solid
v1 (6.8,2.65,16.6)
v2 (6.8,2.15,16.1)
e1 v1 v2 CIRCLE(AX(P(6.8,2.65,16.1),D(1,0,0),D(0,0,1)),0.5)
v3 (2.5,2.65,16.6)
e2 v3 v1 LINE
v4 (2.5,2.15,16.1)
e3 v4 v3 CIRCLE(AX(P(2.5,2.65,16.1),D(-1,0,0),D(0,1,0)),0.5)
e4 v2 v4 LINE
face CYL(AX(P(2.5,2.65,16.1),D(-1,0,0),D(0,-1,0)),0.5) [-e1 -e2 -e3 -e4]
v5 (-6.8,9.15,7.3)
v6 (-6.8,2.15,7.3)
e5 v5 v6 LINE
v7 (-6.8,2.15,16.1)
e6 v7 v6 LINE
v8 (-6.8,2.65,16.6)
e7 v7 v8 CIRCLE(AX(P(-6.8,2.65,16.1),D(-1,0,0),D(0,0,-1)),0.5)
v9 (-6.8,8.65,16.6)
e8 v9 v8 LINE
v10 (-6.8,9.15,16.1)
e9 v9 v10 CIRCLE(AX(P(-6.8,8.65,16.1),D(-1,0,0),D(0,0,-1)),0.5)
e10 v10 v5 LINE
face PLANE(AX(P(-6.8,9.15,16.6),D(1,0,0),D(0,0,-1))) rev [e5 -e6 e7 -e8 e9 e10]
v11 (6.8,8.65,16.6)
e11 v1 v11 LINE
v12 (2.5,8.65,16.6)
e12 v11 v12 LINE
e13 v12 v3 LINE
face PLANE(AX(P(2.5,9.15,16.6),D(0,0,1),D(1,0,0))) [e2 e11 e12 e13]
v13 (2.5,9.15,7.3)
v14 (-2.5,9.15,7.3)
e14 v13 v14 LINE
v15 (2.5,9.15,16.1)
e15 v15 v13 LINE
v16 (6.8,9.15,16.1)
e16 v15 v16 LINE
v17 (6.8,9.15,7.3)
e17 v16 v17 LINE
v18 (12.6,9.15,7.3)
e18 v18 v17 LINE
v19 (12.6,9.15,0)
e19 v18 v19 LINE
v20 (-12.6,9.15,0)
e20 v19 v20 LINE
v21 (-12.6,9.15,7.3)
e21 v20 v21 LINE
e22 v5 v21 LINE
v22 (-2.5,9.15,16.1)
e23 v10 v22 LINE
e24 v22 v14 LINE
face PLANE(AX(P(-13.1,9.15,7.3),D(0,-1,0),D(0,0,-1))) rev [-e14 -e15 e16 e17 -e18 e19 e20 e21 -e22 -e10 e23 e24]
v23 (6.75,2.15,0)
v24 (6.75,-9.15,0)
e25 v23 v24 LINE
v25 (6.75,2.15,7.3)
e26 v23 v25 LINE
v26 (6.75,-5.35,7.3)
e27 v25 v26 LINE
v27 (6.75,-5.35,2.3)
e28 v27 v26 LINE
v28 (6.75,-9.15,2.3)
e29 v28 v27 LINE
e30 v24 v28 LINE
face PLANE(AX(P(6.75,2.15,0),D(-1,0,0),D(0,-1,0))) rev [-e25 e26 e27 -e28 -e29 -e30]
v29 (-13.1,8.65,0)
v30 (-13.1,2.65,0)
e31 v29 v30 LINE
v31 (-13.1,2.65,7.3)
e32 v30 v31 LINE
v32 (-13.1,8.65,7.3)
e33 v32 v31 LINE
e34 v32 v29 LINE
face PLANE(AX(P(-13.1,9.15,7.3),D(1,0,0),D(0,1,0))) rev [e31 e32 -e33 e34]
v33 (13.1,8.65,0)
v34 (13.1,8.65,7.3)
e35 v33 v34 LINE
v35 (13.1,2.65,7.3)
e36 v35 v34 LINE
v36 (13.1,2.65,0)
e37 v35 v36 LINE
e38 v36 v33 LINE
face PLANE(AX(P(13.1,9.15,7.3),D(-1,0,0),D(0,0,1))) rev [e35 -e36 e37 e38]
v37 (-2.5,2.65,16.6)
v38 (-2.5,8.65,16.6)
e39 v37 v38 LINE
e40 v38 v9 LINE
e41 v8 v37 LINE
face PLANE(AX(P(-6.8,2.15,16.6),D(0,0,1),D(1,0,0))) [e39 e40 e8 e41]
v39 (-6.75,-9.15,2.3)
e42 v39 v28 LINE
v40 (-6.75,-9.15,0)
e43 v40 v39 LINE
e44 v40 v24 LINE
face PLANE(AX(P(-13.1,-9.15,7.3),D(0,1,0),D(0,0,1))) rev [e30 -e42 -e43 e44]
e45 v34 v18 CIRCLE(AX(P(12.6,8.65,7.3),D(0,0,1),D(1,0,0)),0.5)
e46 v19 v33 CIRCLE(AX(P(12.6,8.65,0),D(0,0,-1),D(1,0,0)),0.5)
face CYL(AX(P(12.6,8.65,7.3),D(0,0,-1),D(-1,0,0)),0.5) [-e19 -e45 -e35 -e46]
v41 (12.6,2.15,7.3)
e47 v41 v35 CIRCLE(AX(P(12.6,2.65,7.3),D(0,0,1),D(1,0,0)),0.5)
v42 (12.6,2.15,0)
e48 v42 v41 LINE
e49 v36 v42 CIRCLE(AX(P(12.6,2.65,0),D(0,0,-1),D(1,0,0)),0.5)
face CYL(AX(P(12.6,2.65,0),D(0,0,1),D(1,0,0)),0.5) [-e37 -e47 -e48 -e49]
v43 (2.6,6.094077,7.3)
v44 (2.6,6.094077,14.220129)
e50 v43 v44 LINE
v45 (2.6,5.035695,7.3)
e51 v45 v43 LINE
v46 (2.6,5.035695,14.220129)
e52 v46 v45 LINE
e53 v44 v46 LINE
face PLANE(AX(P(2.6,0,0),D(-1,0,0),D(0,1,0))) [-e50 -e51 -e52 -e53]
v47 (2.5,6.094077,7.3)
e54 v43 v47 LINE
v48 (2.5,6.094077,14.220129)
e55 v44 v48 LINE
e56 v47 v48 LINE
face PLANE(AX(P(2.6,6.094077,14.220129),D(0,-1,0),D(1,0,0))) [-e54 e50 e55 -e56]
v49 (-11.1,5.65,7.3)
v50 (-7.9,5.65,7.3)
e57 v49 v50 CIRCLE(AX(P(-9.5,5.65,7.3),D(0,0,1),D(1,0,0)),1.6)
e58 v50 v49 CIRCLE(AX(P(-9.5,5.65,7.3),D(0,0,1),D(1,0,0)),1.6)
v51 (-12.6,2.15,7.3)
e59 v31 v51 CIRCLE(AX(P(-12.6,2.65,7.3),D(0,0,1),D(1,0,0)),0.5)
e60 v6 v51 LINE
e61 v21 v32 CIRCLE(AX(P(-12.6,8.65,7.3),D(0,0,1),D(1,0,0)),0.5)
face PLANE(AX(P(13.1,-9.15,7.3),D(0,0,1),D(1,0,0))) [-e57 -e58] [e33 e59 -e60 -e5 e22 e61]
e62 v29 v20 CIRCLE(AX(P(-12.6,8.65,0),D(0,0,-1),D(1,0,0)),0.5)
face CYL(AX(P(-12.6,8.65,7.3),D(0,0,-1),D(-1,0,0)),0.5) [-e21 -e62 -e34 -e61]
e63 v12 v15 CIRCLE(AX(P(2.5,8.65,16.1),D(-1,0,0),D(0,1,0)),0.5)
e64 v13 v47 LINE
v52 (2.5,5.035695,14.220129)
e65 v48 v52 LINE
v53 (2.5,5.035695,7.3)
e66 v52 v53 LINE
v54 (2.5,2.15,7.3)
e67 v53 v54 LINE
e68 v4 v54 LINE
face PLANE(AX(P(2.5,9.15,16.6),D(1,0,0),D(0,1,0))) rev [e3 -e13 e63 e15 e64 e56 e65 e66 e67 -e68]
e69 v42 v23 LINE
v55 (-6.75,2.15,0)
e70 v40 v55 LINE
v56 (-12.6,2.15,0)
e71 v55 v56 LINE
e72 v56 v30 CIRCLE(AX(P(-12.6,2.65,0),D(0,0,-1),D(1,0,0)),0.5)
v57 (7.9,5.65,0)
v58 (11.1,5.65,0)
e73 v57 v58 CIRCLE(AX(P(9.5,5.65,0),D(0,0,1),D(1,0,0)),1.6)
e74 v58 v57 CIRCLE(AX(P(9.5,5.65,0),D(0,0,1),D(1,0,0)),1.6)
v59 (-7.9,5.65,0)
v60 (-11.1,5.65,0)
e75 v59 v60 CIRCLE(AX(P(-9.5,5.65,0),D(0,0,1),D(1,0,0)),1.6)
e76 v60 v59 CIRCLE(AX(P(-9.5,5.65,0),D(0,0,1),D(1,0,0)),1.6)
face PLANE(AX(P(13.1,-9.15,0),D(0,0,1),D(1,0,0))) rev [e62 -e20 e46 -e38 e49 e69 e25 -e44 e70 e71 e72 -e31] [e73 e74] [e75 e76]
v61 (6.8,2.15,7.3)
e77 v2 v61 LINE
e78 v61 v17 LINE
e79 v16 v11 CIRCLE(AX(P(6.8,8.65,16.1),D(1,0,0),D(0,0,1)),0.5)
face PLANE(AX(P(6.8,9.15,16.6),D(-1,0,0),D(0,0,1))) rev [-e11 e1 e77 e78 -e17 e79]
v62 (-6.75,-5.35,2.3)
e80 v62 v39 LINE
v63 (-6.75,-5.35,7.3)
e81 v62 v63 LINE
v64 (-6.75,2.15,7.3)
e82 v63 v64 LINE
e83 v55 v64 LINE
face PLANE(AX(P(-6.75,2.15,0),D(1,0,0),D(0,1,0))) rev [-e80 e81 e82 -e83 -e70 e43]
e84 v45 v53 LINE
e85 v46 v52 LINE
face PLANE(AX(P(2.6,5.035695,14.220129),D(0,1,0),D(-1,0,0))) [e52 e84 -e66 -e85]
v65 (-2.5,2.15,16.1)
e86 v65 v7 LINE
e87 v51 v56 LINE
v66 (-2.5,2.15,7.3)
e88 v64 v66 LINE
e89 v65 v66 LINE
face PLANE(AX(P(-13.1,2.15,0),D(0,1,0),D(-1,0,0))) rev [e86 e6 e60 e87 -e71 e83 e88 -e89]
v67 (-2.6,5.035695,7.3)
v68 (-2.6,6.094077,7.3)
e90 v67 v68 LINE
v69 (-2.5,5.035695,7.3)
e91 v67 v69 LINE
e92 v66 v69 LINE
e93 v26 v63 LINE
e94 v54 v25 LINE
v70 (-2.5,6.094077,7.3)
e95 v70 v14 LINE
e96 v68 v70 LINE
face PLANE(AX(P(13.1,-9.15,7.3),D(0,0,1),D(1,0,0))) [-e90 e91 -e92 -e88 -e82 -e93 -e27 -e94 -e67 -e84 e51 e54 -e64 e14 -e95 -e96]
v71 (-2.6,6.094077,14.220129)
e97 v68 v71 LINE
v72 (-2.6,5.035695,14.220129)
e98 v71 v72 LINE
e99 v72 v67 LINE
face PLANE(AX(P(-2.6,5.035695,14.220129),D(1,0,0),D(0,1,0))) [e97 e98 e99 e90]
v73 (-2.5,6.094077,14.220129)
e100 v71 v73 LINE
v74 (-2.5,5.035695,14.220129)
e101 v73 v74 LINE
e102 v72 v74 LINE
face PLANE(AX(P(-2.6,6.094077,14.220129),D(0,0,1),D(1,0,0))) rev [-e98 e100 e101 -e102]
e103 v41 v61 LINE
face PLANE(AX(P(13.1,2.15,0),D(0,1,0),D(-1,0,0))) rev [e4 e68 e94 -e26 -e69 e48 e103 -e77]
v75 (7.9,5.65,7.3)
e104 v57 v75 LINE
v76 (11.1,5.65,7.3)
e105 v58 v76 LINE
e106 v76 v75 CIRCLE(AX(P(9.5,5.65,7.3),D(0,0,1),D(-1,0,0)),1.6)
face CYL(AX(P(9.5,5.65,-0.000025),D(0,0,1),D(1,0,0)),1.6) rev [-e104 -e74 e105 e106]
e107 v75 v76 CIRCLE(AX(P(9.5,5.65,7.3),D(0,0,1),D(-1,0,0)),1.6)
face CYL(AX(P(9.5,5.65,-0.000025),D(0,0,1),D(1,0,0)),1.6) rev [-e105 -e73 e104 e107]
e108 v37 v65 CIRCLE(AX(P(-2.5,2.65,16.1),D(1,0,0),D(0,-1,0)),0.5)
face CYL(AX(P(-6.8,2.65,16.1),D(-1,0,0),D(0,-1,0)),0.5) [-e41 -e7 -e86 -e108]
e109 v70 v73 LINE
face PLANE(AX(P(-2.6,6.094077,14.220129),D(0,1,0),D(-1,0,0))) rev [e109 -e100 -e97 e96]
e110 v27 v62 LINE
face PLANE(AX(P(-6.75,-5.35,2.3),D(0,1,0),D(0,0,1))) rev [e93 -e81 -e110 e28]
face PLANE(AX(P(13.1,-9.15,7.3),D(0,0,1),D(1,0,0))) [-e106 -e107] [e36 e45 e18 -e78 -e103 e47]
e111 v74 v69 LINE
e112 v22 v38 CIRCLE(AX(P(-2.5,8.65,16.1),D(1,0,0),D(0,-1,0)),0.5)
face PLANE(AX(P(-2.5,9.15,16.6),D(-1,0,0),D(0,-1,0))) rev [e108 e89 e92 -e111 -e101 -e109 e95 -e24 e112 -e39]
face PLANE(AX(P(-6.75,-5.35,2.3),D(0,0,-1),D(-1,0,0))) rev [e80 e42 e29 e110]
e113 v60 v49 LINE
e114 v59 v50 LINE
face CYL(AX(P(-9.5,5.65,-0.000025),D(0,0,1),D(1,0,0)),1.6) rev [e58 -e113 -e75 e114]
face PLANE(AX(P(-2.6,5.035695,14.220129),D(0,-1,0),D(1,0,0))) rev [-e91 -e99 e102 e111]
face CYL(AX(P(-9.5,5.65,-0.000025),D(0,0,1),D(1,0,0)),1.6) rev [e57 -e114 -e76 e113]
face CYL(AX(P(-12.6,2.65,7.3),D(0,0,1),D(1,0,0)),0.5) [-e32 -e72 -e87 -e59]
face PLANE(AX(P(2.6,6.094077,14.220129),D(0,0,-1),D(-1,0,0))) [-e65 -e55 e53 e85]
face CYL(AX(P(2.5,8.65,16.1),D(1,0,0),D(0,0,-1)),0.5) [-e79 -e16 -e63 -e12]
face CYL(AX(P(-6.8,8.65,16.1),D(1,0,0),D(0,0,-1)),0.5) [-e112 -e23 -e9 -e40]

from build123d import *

# Parameters (mm, degrees)
SKETCH_1_W          = 26.2
SKETCH_1_H          = 18.3
EXTRUDE_1_DEPTH     = 7.3
SKETCH_2_W          = 6.35
SKETCH_2_H          = 11.3
CUT_EXTRUDE_1_DEPTH = 18.567654937
SKETCH_3_W          = 4.3
SKETCH_3_H          = 7
EXTRUDE_2_DEPTH     = 9.3
SKETCH_4_W          = 13.5
SKETCH_4_H          = 3.8
CUT_EXTRUDE_2_DEPTH = 5
SKETCH_5_R          = 1.6
CUT_EXTRUDE_3_DEPTH = 19.488442336
SKETCH_6_W          = 6.920128801
SKETCH_6_H          = 1.058382597
CUT_EXTRUDE_4_DEPTH = 0.1
FILLET_1_R          = 0.5
FILLET_2_R          = 0.5


with BuildPart() as part:
    # 草图1 → 凸台-拉伸1 (new body)
    with BuildSketch(Plane.XY):
        Rectangle(SKETCH_1_W, SKETCH_1_H)
    extrude(amount=EXTRUDE_1_DEPTH)

    # 草图2 → 切除-拉伸1 (cut, through all)
    with BuildSketch(Plane.XY.offset(7.3)):
        with Locations((-9.925, -3.5)):
            Rectangle(SKETCH_2_W, SKETCH_2_H)
        with Locations((9.925, -3.5)):
            Rectangle(SKETCH_2_W, SKETCH_2_H)
    extrude(amount=-CUT_EXTRUDE_1_DEPTH, mode=Mode.SUBTRACT)

    # 草图3 → 凸台-拉伸2 (add)
    with BuildSketch(Plane.XY.offset(7.3)):
        with Locations((-4.65, 5.65)):
            Rectangle(SKETCH_3_W, SKETCH_3_H)
        with Locations((4.65, 5.65)):
            Rectangle(SKETCH_3_W, SKETCH_3_H)
    extrude(amount=EXTRUDE_2_DEPTH)

    # 草图4 → 切除-拉伸2 (cut)
    with BuildSketch(Plane.XY.offset(7.3)):
        with Locations((0, -7.25)):
            Rectangle(SKETCH_4_W, SKETCH_4_H)
    extrude(amount=-CUT_EXTRUDE_2_DEPTH, mode=Mode.SUBTRACT)

    # 草图5 → 切除-拉伸3 (cut, through all)
    with BuildSketch(Plane.XY.offset(7.3)):
        with Locations((-9.5, 5.65)):
            Circle(SKETCH_5_R)
        with Locations((9.5, 5.65)):
            Circle(SKETCH_5_R)
    extrude(amount=-CUT_EXTRUDE_3_DEPTH, mode=Mode.SUBTRACT)

    # 草图6 → 切除-拉伸4 (cut)
    with BuildSketch(Plane(origin=(-2.5, 0, 0), x_dir=(0, 0, -1), z_dir=(1, 0, 0))):
        with Locations((-10.760064401, 5.564886087)):
            Rectangle(SKETCH_6_W, SKETCH_6_H)
    cut_extrude_4 = extrude(amount=-CUT_EXTRUDE_4_DEPTH, mode=Mode.SUBTRACT)

    # 圆角1
    fillet_1_edges = [part.edges().sort_by_distance(p)[0] for p in [
        (13.1, 2.15, 3.65),
        (13.1, 9.15, 3.65),
        (-13.1, 2.15, 3.65),
        (-13.1, 9.15, 3.65),
    ]]
    fillet(fillet_1_edges, radius=FILLET_1_R)

    # 镜向1: 切除-拉伸4 across plane
    add(cut_extrude_4.mirror(Plane(origin=(0, 0, 0), x_dir=(0, 0, 1), z_dir=(1, 0, 0))), mode=Mode.SUBTRACT)

    # 圆角2
    fillet_2_edges = [part.edges().sort_by_distance(p)[0] for p in [
        (4.65, 2.15, 16.6),
        (4.65, 9.15, 16.6),
        (-4.65, 9.15, 16.6),
        (-4.65, 2.15, 16.6),
    ]]
    fillet(fillet_2_edges, radius=FILLET_2_R)


solid = part.part
